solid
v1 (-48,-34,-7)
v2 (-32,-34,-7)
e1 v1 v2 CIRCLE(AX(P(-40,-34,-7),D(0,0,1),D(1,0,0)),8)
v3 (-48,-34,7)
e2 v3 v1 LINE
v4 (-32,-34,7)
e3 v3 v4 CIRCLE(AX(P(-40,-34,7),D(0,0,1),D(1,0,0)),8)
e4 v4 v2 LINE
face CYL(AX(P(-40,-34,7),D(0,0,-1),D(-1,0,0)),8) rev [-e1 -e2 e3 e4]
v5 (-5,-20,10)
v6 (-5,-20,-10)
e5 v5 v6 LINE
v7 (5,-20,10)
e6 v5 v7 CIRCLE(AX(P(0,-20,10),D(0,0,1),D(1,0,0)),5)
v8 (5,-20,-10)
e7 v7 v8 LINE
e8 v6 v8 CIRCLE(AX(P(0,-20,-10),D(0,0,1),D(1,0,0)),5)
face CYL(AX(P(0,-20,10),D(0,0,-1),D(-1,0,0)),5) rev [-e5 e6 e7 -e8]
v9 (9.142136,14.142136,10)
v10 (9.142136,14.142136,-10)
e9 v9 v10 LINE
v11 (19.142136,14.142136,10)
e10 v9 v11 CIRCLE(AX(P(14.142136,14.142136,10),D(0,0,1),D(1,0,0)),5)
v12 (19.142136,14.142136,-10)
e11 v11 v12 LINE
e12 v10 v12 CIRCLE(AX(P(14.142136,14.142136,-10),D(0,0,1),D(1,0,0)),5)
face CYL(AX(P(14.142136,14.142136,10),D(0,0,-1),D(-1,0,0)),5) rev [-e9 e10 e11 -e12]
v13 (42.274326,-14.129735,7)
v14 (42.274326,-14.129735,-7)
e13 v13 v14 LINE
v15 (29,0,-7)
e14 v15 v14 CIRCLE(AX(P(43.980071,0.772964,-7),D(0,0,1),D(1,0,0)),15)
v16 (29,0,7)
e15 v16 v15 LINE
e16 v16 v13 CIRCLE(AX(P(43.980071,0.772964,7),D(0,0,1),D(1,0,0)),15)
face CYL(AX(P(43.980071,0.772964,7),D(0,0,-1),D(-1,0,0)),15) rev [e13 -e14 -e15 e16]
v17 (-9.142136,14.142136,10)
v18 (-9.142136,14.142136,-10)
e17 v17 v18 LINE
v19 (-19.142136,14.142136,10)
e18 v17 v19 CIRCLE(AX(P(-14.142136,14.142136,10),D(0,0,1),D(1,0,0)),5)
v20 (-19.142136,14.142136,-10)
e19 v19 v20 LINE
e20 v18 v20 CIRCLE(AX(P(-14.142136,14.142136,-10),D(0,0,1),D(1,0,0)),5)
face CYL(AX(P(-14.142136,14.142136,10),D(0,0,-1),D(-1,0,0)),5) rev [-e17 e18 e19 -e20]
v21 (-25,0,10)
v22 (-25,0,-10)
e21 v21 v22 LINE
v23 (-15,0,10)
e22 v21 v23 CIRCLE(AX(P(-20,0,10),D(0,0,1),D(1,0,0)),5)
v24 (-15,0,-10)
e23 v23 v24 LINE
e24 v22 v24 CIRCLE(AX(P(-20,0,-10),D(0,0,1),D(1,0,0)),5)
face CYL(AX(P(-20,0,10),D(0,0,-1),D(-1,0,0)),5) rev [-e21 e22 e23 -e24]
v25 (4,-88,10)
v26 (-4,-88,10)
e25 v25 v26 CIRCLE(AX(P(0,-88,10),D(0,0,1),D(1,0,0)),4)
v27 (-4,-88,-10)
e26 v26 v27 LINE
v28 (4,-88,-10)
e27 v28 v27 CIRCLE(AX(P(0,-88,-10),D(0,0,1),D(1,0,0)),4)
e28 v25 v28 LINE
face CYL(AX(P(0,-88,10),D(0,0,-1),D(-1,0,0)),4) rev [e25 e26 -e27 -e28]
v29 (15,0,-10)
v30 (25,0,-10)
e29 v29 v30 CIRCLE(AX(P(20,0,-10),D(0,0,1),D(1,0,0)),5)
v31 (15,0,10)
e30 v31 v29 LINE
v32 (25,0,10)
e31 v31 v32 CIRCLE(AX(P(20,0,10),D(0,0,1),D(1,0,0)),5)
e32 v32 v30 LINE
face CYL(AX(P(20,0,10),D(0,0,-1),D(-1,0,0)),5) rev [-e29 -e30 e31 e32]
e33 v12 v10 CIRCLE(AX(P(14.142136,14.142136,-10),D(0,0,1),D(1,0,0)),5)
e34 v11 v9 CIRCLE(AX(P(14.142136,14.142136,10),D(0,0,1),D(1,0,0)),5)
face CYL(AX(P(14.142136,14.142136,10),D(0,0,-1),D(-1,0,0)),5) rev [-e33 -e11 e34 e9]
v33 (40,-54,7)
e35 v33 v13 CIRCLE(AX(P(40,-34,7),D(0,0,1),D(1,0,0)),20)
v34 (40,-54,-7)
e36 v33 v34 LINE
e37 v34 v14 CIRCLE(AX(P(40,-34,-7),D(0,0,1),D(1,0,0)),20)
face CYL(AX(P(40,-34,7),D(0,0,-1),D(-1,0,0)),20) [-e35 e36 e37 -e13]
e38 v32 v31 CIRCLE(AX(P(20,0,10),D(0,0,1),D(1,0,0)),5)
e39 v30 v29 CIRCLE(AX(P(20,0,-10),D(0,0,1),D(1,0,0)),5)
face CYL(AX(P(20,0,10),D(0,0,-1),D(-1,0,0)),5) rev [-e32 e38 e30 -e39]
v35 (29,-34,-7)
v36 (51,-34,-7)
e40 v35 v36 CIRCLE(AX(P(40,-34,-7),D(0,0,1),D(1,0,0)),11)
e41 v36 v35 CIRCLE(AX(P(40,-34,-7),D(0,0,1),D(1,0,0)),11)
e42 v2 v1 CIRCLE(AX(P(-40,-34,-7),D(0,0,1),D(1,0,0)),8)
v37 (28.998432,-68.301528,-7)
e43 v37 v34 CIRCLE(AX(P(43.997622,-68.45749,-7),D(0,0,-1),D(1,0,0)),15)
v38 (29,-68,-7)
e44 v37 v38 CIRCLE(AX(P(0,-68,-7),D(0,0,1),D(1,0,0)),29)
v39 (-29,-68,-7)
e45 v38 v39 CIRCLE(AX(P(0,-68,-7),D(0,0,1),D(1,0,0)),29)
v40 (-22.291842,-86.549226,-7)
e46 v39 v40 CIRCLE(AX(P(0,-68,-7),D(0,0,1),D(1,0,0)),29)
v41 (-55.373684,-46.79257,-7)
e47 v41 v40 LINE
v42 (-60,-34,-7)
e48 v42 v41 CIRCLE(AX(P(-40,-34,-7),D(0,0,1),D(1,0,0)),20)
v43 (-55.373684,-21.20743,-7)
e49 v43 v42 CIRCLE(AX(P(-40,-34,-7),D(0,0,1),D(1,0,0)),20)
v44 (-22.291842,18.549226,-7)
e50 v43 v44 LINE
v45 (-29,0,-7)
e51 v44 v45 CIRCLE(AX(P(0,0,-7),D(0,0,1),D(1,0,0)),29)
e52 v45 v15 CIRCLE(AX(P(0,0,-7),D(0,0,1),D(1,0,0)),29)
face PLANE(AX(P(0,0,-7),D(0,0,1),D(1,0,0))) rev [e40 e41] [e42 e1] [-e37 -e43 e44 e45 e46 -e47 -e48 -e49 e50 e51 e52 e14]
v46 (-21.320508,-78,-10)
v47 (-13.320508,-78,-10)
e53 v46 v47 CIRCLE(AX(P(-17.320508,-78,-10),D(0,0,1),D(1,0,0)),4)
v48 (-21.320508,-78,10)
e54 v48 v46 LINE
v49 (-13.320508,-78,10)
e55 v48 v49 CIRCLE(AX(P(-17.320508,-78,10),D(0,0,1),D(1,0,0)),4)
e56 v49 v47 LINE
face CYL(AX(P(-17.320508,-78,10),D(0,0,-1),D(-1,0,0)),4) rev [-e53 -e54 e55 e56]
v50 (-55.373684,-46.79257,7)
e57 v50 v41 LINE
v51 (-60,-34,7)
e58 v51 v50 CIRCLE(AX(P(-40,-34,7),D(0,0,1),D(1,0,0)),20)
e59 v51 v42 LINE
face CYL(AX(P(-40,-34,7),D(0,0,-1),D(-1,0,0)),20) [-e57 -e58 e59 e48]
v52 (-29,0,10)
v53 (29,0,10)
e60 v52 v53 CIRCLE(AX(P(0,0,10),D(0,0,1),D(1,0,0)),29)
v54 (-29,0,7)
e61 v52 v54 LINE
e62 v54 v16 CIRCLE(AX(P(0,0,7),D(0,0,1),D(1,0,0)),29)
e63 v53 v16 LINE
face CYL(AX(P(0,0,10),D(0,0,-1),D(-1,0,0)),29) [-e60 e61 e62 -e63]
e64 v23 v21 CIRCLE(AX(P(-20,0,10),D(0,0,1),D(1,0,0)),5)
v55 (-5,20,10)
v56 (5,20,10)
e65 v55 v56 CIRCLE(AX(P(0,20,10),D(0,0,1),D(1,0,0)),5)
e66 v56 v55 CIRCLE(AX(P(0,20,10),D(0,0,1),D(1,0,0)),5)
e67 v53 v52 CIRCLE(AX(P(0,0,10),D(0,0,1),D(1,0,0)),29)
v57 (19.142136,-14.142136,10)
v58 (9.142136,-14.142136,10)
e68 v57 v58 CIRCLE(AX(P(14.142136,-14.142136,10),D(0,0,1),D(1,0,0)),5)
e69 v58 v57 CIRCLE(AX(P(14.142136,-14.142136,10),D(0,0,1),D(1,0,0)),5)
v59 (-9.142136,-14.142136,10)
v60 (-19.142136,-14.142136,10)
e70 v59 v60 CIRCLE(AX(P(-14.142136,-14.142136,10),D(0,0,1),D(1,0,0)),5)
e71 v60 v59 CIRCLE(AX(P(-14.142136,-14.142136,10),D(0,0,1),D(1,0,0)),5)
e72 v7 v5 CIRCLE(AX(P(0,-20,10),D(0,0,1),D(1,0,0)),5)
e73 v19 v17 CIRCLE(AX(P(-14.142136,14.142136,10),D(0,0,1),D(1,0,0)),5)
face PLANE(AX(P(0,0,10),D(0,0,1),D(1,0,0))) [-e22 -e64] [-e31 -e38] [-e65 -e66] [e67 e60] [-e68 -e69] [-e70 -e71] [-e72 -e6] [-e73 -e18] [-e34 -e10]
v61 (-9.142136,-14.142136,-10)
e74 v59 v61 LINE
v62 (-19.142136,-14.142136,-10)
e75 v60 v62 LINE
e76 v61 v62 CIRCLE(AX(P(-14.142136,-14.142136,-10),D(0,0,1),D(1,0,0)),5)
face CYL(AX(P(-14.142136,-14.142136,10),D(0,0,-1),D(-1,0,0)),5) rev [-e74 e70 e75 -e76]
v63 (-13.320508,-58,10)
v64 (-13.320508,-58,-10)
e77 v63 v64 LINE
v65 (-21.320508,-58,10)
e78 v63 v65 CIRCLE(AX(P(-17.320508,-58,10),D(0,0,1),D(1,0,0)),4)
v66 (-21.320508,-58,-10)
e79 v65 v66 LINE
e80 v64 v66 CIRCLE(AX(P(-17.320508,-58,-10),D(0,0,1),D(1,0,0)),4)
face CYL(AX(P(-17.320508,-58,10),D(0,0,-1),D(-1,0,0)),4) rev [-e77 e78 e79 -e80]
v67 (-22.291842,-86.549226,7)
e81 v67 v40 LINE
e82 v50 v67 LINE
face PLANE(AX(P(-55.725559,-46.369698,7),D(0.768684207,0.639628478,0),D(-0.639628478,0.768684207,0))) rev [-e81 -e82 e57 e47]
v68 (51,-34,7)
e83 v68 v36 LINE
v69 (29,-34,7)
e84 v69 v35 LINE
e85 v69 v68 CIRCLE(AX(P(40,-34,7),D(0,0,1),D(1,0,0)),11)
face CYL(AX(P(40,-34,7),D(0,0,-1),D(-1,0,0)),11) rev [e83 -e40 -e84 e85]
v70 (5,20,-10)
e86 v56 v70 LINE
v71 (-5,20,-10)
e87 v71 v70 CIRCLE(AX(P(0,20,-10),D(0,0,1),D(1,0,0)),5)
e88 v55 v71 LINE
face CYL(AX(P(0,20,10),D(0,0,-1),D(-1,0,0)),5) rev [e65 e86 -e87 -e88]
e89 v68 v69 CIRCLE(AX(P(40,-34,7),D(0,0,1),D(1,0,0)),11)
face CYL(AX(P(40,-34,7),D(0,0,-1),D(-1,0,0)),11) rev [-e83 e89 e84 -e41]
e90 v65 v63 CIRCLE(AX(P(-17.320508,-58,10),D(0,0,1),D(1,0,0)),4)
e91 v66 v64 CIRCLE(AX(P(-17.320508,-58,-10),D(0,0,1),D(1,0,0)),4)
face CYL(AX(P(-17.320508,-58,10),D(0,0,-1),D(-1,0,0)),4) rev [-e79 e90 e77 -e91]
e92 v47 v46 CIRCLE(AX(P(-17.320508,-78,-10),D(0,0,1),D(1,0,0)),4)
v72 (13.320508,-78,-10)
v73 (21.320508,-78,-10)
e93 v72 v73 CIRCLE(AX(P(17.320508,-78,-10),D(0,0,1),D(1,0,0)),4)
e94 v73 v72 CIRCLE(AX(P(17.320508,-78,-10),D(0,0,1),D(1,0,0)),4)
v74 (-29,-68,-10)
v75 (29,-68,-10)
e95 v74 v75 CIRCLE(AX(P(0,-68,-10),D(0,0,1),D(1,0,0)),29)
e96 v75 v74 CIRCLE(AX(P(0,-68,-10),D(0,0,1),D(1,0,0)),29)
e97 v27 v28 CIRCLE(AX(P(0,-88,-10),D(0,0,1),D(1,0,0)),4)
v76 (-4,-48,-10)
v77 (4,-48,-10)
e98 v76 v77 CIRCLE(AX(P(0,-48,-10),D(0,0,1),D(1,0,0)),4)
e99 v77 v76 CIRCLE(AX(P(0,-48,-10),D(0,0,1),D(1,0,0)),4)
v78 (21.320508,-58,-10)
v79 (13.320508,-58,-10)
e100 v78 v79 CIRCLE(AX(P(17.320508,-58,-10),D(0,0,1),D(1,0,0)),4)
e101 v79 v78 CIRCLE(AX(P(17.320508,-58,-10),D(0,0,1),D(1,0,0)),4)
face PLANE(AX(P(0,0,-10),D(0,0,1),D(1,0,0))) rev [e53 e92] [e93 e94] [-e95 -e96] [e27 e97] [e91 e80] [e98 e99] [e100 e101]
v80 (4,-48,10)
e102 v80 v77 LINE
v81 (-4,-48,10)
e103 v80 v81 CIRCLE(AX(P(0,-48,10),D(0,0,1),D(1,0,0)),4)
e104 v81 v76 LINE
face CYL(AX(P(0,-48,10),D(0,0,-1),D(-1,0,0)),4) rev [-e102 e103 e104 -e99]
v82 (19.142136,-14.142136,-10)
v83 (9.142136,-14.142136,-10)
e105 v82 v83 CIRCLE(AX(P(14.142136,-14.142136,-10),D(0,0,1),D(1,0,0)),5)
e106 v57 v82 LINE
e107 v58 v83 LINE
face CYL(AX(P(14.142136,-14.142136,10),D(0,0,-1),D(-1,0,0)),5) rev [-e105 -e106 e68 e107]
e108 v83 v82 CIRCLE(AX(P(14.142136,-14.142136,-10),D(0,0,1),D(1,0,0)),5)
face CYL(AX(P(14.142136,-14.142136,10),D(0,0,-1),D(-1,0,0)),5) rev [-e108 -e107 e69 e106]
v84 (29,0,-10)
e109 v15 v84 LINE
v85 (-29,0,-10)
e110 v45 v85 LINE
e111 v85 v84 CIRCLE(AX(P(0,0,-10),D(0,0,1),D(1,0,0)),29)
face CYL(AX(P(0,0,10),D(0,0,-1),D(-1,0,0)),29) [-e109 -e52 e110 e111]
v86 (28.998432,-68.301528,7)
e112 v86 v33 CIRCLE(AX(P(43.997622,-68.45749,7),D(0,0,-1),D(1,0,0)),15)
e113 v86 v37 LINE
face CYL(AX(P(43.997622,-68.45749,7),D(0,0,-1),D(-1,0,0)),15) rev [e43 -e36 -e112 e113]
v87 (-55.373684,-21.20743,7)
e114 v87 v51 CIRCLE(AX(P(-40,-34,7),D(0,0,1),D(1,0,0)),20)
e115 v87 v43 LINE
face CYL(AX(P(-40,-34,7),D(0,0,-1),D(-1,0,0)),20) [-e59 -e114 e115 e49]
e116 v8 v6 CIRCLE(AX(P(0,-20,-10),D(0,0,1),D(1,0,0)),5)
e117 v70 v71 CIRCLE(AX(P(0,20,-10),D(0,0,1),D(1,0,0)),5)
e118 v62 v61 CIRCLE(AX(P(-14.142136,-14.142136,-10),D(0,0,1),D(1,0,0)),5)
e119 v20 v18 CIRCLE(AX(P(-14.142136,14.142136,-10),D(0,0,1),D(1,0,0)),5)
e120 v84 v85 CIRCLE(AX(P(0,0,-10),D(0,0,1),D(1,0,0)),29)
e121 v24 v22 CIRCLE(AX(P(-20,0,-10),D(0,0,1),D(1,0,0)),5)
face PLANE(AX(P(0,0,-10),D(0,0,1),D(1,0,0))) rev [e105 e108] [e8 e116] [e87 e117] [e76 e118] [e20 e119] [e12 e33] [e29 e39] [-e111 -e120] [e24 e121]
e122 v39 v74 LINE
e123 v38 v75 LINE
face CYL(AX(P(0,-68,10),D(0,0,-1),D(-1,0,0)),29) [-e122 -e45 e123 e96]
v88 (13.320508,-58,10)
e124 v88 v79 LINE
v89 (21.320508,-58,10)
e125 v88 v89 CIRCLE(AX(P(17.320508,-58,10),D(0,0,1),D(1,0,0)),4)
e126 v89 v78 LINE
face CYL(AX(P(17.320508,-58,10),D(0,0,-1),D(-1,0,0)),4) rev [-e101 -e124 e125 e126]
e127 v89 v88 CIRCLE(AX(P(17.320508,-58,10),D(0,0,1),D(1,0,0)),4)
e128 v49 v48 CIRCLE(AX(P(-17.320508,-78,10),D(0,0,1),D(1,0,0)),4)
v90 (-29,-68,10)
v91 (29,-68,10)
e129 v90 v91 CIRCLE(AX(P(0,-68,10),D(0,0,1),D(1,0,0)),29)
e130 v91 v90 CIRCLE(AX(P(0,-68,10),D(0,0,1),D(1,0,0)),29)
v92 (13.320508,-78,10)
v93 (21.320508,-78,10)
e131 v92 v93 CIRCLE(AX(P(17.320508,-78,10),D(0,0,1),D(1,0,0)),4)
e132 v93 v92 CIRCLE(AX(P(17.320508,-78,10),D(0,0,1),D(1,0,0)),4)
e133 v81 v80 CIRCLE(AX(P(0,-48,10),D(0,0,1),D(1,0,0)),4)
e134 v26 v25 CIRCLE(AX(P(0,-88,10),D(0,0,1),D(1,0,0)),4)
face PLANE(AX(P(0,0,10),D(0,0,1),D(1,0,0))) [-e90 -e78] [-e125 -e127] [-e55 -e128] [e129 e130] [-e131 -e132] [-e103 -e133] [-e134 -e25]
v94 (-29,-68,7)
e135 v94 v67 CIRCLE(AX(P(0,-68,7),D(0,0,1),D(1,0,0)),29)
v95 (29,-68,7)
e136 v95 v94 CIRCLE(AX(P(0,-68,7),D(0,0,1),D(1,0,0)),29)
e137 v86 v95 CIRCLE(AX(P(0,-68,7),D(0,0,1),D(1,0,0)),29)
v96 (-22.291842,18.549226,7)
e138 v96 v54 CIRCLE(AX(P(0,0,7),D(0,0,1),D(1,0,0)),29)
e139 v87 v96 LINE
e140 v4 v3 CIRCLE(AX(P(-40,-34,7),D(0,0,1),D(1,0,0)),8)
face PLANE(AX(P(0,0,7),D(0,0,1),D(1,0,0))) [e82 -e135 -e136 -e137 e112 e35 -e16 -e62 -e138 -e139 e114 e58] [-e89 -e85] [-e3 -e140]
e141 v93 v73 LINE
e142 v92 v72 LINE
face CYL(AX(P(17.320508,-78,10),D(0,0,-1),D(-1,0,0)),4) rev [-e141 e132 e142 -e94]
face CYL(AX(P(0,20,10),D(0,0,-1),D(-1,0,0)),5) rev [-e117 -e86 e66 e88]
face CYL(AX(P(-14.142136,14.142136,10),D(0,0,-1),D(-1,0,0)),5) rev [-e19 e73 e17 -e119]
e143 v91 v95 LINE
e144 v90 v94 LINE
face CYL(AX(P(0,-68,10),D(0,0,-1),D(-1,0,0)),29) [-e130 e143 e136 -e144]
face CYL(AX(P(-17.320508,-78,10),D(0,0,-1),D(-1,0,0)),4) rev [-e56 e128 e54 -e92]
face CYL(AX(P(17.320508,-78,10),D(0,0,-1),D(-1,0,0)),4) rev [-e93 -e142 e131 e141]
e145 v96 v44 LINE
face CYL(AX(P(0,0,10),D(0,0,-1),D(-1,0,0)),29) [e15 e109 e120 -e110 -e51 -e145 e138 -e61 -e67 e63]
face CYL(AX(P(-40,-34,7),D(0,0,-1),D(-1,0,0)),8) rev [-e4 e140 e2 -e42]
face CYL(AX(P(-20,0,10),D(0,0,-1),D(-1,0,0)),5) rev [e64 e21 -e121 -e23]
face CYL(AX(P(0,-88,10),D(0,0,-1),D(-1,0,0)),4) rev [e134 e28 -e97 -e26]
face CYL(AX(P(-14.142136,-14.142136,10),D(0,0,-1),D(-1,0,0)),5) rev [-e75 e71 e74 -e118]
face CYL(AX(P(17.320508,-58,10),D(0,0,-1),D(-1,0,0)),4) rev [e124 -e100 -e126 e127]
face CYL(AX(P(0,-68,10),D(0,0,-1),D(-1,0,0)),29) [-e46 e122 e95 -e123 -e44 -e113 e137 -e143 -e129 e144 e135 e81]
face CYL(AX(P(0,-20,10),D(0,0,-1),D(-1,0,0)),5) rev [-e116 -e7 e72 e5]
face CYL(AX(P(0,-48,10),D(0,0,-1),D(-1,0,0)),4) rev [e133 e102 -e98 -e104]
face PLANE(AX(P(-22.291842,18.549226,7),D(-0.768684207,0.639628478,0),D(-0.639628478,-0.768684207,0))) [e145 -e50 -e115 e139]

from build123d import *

# Parameters (mm, degrees)
TRI_LOBE_PLATE_PROFILE_R          = 29
TRI_LOBE_PLATE_PROFILE_R_2        = 5
LOBE_PADS_EXTRUDE_20MM_DEPTH      = 10
TRI_LOBE_PLATE_PROFILE_R_3        = 4
LOBE_PADS_EXTRUDE_20MM_2_DEPTH    = 10
SKETCH1_3_R                       = 8
SKETCH1_3_R_2                     = 11
CONNECTING_WEB_EXTRUDE_14MM_DEPTH = 7


with BuildPart() as part:
    # Tri-Lobe Plate Profile → Lobe Pads Extrude 20mm (new, symmetric)
    with BuildSketch(Plane.XY):
        Circle(TRI_LOBE_PLATE_PROFILE_R)
        with Locations((-14.142135624, 14.142135624)):
            Circle(TRI_LOBE_PLATE_PROFILE_R_2, mode=Mode.SUBTRACT)
        with Locations((-20, 0)):
            Circle(TRI_LOBE_PLATE_PROFILE_R_2, mode=Mode.SUBTRACT)
        with Locations((-14.142135624, -14.142135624)):
            Circle(TRI_LOBE_PLATE_PROFILE_R_2, mode=Mode.SUBTRACT)
        with Locations((0, -20)):
            Circle(TRI_LOBE_PLATE_PROFILE_R_2, mode=Mode.SUBTRACT)
        with Locations((14.142135624, -14.142135624)):
            Circle(TRI_LOBE_PLATE_PROFILE_R_2, mode=Mode.SUBTRACT)
        with Locations((20, 0)):
            Circle(TRI_LOBE_PLATE_PROFILE_R_2, mode=Mode.SUBTRACT)
        with Locations((14.142135624, 14.142135624)):
            Circle(TRI_LOBE_PLATE_PROFILE_R_2, mode=Mode.SUBTRACT)
        with Locations((0, 20)):
            Circle(TRI_LOBE_PLATE_PROFILE_R_2, mode=Mode.SUBTRACT)
    extrude(amount=LOBE_PADS_EXTRUDE_20MM_DEPTH, both=True)



with BuildPart() as body_2:
    # Tri-Lobe Plate Profile → Lobe Pads Extrude 20mm 2 (new, symmetric)
    with BuildSketch(Plane.XY):
        with Locations((0, -68)):
            Circle(TRI_LOBE_PLATE_PROFILE_R)
        with Locations((17.320508076, -78)):
            Circle(TRI_LOBE_PLATE_PROFILE_R_3, mode=Mode.SUBTRACT)
        with Locations((17.320508076, -58)):
            Circle(TRI_LOBE_PLATE_PROFILE_R_3, mode=Mode.SUBTRACT)
        with Locations((0, -48)):
            Circle(TRI_LOBE_PLATE_PROFILE_R_3, mode=Mode.SUBTRACT)
        with Locations((-17.320508076, -58)):
            Circle(TRI_LOBE_PLATE_PROFILE_R_3, mode=Mode.SUBTRACT)
        with Locations((-17.320508076, -78)):
            Circle(TRI_LOBE_PLATE_PROFILE_R_3, mode=Mode.SUBTRACT)
        with Locations((0, -88)):
            Circle(TRI_LOBE_PLATE_PROFILE_R_3, mode=Mode.SUBTRACT)
    extrude(amount=LOBE_PADS_EXTRUDE_20MM_2_DEPTH, both=True)


with BuildPart() as part_1:
    add(part.part)

    add(body_2.part)  # Connecting Web Extrude 14mm merges body 2
    # Sketch1_3 → Connecting Web Extrude 14mm (add, symmetric)
    with BuildSketch(Plane.XY):
        with BuildLine():
            Line((-22.291841993, 18.549225875), (-55.373684133, -21.207430431))
            ThreePointArc((-55.373684133, -21.207430431), (-60, -34), (-55.373684133, -46.792569569))
            Line((-55.373684133, -46.792569569), (-22.291841993, -86.549225875))
            ThreePointArc((-22.291841993, -86.549225875), (-9.862468813, -40.728555064), (29, -68))
            ThreePointArc((29, -68), (28.999608095, -68.150765842), (28.99843239, -68.301527609))
            ThreePointArc((28.99843239, -68.301527609), (32.108419422, -59.311623745), (40, -54))
            ThreePointArc((40, -54), (59.967539964, -35.139011754), (42.274326272, -14.129734778))
            ThreePointArc((42.274326272, -14.129734778), (33.047712472, -9.497553742), (29, 0))
            ThreePointArc((29, 0), (-9.862468813, -27.271444936), (-22.291841993, 18.549225875))
        make_face()
        with Locations((-40, -34)):
            Circle(SKETCH1_3_R, mode=Mode.SUBTRACT)
        with Locations((40, -34)):
            Circle(SKETCH1_3_R_2, mode=Mode.SUBTRACT)
    extrude(amount=CONNECTING_WEB_EXTRUDE_14MM_DEPTH, both=True)


solid = part_1.part
